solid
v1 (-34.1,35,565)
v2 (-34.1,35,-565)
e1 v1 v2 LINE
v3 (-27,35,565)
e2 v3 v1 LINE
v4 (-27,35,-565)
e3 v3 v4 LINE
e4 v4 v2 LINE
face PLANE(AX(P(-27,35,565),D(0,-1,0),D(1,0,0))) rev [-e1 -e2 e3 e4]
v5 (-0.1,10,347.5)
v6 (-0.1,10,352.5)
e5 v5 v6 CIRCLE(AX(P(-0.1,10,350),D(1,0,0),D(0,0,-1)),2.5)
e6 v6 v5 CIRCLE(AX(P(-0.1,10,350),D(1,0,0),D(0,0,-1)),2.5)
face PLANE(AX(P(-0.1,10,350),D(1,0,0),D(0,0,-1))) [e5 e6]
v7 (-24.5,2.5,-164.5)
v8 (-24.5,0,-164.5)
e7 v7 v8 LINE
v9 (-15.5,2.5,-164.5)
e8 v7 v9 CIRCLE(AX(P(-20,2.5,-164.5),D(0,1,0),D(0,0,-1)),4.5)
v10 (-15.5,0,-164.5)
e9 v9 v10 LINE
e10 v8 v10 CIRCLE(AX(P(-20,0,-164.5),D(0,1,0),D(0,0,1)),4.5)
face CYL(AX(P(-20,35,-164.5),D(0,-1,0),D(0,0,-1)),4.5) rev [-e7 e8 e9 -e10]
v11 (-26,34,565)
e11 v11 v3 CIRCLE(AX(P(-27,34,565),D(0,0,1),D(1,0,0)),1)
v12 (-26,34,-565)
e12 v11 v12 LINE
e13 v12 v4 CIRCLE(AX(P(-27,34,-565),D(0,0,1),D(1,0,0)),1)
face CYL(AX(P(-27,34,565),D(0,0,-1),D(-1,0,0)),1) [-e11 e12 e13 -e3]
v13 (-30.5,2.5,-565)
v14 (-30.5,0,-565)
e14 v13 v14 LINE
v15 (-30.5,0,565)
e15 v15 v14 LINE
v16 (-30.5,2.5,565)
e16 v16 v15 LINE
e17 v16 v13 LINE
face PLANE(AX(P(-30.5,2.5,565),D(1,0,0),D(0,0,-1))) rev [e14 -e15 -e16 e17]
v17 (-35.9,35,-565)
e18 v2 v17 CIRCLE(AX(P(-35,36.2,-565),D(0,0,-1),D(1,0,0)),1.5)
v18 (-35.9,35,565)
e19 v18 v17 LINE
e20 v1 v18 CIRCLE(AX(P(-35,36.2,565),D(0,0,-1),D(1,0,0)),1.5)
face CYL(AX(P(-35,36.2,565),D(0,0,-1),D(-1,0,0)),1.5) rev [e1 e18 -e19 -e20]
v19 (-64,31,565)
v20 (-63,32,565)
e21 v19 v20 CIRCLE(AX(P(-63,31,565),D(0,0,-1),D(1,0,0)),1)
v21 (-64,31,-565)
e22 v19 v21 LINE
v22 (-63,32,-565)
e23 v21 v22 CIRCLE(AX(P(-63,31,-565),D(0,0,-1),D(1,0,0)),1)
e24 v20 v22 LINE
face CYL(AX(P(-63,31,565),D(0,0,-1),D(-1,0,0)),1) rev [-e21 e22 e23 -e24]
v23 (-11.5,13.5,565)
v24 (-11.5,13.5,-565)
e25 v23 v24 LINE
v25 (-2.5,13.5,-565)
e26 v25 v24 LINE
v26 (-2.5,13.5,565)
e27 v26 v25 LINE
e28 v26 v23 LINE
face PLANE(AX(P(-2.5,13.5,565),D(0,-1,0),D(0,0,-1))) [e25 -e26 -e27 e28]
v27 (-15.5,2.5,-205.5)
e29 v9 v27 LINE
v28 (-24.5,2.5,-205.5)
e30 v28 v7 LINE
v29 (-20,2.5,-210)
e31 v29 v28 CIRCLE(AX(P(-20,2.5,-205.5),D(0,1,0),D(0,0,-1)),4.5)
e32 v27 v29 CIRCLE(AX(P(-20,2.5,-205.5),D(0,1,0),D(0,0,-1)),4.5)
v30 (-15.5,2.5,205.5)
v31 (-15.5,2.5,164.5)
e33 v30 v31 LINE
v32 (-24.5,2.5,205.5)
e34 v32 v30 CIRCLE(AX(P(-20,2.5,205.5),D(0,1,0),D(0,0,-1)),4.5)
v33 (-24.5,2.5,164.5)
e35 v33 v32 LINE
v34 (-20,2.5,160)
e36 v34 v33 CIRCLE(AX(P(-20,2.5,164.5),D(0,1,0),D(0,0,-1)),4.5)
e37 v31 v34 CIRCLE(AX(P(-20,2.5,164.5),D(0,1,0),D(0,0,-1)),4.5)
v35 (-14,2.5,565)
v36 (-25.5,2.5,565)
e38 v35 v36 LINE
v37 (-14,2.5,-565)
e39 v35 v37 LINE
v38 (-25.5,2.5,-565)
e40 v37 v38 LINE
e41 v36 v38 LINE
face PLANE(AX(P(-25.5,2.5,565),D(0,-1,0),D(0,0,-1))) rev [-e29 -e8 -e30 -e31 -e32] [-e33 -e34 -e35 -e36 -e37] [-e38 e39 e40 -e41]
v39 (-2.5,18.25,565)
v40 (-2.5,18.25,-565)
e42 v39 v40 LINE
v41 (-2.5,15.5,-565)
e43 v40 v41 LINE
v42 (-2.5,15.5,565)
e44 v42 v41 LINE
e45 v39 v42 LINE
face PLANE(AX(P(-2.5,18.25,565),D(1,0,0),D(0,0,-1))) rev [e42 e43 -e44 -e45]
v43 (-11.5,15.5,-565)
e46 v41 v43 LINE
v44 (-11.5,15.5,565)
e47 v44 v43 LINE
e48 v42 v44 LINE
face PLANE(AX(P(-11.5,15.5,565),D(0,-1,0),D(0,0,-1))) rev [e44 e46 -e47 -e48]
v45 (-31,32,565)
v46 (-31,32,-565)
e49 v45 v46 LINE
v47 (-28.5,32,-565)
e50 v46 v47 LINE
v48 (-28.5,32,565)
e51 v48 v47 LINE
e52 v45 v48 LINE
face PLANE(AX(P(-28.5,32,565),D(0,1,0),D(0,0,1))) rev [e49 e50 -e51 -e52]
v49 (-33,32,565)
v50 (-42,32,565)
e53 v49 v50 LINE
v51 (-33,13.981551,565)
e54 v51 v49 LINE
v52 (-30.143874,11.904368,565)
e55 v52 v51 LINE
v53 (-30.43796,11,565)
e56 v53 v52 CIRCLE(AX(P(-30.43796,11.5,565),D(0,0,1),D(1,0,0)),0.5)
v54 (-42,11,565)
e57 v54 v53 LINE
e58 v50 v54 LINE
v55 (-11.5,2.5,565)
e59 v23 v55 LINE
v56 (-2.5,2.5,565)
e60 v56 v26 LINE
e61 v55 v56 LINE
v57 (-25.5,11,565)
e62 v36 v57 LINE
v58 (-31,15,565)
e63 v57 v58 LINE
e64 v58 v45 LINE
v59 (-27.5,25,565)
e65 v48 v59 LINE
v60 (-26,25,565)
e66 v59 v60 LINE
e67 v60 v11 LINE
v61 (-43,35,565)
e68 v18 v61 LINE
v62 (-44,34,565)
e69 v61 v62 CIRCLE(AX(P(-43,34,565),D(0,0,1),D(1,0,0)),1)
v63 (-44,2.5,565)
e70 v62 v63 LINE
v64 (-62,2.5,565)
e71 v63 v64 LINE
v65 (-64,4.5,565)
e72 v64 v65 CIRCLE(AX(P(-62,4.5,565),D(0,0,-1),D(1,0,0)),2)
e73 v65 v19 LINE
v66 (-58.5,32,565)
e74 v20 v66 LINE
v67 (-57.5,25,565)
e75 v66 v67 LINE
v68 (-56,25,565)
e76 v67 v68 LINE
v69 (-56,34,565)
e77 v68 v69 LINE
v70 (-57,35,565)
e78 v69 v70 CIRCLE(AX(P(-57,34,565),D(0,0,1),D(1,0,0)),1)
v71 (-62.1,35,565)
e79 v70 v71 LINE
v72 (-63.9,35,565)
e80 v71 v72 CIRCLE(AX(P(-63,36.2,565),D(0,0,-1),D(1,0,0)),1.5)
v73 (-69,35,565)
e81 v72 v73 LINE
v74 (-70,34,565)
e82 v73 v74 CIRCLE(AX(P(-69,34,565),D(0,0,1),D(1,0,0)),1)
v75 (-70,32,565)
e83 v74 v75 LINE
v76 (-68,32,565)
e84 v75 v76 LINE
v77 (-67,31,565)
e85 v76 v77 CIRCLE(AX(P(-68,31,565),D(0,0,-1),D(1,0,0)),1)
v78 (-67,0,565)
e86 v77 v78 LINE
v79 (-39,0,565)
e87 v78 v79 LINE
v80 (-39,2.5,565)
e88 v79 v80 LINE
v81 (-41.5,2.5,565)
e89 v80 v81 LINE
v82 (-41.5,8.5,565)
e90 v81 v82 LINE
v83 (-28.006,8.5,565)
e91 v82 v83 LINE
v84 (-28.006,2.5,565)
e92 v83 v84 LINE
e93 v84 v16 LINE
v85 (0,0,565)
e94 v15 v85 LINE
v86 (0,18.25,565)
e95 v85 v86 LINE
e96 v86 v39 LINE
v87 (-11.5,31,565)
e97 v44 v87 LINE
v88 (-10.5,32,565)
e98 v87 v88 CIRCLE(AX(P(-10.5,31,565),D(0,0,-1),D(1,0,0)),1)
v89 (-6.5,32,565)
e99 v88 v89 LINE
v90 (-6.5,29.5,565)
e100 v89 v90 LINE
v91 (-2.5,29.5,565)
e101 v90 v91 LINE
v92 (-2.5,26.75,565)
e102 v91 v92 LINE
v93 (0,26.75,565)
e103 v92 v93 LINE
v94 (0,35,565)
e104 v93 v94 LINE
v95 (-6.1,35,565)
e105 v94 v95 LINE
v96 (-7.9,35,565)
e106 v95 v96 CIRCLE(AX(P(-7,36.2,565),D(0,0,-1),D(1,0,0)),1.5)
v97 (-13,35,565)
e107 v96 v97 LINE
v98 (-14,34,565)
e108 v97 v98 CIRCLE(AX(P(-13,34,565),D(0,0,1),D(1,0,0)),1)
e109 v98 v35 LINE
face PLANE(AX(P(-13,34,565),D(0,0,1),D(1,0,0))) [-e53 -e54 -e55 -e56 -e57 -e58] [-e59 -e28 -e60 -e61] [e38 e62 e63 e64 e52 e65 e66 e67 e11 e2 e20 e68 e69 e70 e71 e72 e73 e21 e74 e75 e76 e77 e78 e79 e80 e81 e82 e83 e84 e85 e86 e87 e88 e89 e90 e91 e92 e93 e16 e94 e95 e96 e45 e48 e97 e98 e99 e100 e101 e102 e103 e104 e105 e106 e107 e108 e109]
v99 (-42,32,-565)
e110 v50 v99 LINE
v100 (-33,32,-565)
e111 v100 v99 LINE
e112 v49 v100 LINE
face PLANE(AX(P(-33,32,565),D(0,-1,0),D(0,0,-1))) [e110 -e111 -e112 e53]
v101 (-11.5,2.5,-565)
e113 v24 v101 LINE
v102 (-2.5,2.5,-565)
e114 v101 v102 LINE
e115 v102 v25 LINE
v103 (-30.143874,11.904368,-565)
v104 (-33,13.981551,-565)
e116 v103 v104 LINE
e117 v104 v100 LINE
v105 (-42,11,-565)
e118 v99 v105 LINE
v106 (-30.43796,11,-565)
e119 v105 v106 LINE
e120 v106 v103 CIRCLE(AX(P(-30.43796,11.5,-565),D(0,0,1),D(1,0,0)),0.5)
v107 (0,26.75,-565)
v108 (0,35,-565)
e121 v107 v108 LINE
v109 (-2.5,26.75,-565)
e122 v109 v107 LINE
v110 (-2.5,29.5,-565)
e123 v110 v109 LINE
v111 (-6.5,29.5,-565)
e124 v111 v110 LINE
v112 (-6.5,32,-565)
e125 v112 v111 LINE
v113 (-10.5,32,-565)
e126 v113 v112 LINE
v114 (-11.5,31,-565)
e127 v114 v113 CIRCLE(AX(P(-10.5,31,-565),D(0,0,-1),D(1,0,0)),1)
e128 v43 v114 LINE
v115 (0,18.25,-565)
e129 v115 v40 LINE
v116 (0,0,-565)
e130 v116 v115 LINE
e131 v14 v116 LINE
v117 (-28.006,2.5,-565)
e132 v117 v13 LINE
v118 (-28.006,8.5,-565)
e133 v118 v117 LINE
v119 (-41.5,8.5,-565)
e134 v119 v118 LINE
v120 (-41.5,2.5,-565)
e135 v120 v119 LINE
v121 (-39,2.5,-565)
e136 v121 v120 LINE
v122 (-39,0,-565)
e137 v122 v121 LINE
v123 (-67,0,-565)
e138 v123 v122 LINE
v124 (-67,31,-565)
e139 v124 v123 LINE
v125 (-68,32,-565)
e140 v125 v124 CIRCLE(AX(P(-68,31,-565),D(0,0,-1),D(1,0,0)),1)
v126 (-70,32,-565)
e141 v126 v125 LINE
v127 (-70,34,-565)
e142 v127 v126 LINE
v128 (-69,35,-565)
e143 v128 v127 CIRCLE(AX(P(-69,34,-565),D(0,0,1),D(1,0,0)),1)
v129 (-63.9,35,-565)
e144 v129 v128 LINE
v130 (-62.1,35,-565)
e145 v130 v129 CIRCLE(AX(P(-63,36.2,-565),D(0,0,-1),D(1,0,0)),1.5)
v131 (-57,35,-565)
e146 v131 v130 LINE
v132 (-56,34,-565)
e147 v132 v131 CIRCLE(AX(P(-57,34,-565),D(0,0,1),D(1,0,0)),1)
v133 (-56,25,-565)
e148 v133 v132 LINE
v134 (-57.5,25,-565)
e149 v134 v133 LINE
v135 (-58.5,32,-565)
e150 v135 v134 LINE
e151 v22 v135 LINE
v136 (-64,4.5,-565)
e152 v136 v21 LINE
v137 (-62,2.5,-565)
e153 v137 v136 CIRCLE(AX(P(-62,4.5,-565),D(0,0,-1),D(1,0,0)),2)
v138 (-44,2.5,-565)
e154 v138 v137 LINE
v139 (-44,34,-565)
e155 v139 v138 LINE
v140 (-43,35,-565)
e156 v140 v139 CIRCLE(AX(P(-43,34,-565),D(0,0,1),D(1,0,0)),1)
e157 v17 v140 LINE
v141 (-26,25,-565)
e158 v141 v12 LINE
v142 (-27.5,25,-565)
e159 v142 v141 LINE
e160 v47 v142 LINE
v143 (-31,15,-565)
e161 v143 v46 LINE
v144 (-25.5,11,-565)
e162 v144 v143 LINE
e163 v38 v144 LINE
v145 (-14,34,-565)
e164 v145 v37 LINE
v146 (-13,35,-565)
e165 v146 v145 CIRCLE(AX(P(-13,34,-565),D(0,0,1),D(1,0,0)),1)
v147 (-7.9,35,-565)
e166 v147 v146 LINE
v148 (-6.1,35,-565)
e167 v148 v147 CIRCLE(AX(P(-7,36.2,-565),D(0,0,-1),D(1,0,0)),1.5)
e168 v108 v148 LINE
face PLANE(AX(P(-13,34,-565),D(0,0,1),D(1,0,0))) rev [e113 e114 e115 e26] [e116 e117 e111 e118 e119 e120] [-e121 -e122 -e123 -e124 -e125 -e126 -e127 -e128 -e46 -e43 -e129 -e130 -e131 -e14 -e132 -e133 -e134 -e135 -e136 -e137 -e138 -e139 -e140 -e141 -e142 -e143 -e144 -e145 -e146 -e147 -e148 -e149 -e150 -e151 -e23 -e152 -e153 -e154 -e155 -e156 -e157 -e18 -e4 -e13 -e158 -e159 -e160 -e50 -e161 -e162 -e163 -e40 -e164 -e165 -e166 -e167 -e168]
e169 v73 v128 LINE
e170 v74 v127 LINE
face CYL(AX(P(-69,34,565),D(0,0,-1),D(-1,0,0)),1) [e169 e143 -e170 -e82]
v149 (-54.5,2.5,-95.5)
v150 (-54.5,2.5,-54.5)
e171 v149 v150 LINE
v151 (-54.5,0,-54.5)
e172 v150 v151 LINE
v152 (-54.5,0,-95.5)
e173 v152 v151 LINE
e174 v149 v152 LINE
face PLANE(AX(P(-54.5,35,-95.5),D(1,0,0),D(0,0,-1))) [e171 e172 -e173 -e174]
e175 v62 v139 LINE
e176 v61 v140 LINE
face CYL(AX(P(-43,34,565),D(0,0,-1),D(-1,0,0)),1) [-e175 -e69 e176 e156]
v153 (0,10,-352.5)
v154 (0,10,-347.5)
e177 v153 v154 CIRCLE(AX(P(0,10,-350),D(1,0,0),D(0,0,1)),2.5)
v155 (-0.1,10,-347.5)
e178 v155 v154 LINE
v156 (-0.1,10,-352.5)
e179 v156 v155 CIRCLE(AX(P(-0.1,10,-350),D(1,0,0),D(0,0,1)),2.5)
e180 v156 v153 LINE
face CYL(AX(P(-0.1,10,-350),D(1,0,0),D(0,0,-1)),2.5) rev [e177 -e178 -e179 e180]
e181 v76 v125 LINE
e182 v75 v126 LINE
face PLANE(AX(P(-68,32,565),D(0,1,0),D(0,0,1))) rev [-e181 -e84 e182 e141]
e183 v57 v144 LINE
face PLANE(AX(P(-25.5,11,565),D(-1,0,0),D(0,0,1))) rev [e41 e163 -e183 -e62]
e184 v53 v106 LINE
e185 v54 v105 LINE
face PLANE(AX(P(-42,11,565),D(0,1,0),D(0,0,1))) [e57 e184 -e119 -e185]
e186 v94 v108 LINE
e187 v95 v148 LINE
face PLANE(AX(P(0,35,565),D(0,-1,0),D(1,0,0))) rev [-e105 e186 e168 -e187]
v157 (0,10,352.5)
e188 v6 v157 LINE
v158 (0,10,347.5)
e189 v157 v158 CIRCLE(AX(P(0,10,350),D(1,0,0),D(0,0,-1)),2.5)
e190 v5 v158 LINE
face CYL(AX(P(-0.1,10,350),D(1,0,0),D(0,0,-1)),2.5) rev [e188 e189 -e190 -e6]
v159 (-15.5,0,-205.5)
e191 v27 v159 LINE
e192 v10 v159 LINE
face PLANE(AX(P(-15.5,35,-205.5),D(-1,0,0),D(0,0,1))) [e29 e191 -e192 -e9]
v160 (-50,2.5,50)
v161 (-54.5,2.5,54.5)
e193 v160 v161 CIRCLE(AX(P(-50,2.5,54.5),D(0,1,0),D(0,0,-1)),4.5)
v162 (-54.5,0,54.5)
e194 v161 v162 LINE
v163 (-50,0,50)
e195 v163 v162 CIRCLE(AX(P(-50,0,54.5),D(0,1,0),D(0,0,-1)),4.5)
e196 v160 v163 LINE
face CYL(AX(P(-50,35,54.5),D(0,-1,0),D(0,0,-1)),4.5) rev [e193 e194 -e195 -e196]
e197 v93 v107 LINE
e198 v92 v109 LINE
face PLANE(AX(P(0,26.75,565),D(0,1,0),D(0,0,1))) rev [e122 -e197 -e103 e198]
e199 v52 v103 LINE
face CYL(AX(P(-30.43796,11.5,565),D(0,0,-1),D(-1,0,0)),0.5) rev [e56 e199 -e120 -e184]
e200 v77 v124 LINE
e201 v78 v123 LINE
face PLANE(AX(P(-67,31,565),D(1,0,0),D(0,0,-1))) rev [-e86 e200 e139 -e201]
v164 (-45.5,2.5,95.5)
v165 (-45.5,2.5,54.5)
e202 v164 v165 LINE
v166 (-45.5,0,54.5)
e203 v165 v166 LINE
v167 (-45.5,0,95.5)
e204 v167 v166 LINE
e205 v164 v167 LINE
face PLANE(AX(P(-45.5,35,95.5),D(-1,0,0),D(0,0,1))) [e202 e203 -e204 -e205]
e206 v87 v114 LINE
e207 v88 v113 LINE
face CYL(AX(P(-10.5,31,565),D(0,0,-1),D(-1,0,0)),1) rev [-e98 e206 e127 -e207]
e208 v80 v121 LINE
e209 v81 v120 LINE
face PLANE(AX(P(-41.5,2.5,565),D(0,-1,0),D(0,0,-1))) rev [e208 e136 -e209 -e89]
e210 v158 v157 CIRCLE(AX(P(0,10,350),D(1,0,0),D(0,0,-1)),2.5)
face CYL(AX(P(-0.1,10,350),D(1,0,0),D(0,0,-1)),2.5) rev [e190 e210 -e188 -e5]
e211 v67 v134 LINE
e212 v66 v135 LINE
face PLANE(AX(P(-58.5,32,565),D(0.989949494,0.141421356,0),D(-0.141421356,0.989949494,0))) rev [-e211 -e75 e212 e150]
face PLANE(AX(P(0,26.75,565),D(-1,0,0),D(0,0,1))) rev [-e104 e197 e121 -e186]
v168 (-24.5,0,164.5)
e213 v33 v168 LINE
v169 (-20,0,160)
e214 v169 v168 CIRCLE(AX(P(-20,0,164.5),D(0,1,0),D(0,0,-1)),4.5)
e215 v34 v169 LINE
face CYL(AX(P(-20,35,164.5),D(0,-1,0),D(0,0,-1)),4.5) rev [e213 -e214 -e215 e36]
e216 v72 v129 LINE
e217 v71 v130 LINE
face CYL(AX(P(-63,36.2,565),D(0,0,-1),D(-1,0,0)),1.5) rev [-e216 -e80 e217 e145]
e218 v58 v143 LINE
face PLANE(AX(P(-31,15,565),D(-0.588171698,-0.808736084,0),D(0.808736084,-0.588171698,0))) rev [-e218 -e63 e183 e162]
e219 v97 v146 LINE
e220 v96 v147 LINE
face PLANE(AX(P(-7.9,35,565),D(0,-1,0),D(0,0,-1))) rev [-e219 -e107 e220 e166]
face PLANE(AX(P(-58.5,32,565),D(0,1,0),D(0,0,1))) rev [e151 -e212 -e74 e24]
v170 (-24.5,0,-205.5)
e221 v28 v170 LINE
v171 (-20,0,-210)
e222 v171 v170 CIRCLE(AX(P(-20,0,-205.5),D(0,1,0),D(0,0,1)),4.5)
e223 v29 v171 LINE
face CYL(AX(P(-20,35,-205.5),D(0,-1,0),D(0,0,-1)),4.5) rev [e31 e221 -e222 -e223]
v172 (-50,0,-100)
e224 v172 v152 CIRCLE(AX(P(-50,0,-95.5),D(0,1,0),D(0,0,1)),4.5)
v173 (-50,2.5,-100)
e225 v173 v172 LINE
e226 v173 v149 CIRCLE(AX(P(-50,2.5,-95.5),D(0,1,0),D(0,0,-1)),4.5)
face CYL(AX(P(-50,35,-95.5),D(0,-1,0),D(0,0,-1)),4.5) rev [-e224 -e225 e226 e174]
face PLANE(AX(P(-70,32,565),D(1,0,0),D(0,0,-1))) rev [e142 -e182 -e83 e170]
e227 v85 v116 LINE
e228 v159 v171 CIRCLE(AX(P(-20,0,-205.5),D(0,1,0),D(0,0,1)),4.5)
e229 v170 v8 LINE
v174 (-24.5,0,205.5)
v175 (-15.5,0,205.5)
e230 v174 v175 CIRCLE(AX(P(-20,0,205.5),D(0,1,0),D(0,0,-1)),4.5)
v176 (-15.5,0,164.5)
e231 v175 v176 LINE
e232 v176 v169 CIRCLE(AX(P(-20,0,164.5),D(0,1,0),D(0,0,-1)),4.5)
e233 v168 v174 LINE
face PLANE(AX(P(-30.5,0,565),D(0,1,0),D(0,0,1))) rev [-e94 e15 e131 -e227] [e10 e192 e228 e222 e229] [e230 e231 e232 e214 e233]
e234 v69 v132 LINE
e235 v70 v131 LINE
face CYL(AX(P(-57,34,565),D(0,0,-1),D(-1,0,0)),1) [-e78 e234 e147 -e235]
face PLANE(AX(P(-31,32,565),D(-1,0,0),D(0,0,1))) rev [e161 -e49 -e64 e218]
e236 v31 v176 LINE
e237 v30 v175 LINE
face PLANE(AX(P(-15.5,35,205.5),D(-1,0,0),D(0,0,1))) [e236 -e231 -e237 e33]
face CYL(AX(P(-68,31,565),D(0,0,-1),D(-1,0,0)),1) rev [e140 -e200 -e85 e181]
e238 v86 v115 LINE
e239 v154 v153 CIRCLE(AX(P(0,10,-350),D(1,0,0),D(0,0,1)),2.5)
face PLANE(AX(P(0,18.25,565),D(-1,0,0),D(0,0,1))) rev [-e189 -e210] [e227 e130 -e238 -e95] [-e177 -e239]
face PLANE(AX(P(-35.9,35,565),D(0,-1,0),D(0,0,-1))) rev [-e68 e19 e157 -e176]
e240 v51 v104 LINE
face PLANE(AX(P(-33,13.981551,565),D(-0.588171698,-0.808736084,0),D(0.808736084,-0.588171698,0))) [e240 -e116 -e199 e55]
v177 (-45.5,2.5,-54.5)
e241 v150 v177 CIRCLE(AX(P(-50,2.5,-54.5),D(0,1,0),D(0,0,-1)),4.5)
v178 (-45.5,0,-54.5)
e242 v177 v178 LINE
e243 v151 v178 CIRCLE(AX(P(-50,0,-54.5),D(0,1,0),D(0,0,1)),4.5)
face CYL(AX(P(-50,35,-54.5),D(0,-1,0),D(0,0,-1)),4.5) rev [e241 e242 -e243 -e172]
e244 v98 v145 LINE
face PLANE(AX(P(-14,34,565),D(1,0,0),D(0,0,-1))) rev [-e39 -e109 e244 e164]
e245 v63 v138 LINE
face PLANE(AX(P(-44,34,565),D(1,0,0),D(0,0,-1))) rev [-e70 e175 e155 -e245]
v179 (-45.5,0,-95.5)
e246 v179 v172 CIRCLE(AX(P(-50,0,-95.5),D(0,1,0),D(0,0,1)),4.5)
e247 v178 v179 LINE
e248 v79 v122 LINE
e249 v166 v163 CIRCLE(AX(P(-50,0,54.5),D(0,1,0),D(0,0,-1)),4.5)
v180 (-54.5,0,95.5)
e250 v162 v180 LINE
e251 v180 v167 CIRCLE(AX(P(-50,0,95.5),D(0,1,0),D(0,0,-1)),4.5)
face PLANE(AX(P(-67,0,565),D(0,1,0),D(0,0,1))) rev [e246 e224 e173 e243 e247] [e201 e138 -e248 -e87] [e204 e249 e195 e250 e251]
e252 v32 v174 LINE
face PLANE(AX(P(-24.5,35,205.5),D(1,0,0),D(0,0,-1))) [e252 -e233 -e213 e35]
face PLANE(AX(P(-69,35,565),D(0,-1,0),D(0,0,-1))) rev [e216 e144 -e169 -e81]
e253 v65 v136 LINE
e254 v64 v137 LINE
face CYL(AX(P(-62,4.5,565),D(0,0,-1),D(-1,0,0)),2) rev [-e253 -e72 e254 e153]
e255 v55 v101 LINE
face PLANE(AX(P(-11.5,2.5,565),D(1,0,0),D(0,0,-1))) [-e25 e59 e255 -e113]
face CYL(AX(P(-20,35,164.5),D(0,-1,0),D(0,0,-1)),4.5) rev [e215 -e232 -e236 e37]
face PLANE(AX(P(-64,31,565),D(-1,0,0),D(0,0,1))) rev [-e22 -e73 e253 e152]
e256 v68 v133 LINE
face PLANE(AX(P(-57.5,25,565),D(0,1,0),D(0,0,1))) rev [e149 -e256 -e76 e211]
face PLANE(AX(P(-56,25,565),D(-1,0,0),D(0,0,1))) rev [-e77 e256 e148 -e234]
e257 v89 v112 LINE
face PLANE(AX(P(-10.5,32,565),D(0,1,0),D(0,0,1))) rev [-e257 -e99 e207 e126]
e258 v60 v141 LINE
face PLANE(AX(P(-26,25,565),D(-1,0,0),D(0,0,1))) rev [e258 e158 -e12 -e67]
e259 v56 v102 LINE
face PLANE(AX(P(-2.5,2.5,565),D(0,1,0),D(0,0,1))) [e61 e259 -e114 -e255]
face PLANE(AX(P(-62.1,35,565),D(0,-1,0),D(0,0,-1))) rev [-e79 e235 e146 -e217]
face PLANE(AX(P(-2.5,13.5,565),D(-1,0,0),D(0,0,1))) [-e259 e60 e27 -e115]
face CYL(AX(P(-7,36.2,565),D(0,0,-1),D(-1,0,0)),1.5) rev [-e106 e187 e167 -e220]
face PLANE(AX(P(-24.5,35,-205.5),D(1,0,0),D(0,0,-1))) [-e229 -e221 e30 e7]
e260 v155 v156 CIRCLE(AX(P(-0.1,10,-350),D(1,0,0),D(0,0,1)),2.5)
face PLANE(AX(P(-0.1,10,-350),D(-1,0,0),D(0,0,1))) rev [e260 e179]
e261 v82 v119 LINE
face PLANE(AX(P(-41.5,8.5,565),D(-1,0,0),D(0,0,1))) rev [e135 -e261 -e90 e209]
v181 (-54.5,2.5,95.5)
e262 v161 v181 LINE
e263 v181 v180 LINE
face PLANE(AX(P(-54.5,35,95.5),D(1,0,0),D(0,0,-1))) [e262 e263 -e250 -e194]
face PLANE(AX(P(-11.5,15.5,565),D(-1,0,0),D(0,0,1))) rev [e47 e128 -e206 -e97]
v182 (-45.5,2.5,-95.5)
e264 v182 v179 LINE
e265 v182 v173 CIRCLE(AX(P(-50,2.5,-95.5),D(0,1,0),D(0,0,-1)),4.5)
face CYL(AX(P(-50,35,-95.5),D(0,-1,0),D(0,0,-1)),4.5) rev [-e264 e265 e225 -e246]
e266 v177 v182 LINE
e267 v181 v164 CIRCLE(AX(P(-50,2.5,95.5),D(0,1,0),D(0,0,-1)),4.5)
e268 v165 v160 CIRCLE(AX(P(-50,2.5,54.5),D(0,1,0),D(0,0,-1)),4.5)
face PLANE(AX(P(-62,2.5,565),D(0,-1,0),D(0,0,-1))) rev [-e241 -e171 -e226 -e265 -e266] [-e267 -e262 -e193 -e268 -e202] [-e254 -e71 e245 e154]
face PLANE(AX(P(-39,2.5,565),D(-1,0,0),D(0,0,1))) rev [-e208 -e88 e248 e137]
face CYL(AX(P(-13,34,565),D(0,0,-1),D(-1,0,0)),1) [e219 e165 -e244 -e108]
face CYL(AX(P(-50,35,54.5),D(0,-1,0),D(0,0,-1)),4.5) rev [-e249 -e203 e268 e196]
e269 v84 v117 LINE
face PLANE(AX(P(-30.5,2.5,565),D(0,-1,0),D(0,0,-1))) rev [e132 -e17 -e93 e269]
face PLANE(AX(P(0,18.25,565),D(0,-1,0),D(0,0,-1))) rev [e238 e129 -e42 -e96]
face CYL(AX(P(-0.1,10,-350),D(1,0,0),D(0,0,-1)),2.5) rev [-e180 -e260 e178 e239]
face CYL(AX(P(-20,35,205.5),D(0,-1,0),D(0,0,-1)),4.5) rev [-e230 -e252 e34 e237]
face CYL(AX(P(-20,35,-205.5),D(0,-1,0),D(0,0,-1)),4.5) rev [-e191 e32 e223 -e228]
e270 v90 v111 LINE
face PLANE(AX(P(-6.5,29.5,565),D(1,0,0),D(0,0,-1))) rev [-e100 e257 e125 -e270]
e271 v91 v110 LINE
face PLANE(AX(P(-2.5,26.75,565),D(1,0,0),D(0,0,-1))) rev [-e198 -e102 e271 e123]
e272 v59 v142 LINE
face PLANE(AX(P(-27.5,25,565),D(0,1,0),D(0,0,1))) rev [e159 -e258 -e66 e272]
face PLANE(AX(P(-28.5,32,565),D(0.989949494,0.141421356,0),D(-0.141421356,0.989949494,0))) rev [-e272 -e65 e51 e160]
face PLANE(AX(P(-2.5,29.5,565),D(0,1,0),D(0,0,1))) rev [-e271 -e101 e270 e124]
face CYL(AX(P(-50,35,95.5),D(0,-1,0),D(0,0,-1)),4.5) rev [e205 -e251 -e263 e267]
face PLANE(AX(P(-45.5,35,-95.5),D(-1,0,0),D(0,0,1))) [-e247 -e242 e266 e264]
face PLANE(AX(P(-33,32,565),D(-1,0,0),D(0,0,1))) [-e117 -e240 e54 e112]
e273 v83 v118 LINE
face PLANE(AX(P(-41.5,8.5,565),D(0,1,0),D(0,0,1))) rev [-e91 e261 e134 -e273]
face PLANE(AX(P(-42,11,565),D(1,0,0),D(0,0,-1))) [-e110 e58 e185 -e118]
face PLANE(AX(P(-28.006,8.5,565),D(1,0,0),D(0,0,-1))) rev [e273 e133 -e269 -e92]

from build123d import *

# Parameters (mm, degrees)
SKETCH_1_W               = 9
SKETCH_1_H               = 11
EXTRUDE_1_DEPTH          = 565
CUT_EXTRUDE_1_DEPTH      = 571.246657158
CUT_EXTRUDE_1_DEPTH_BACK = 571.246657158
SKETCH_3_R               = 2.5
CUT_EXTRUDE_2_DEPTH      = 0.1


with BuildPart() as part:
    # 草图1 → 凸台-拉伸1 (new, symmetric)
    with BuildSketch(Plane.XY):
        with BuildLine():
            Line((-28.5, 32), (-27.5, 25))
            Line((-27.5, 25), (-26, 25))
            Line((-26, 25), (-26, 34))
            ThreePointArc((-26, 34), (-26.292893219, 34.707106781), (-27, 35))
            Line((-27, 35), (-34.1, 35))
            ThreePointArc((-34.1, 35), (-35, 34.7), (-35.9, 35))
            Line((-35.9, 35), (-43, 35))
            ThreePointArc((-43, 35), (-43.707106781, 34.707106781), (-44, 34))
            Line((-44, 34), (-44, 2.5))
            Line((-44, 2.5), (-62, 2.5))
            ThreePointArc((-62, 2.5), (-63.414213562, 3.085786438), (-64, 4.5))
            Line((-64, 4.5), (-64, 31))
            ThreePointArc((-64, 31), (-63.707106781, 31.707106781), (-63, 32))
            Line((-63, 32), (-58.5, 32))
            Line((-58.5, 32), (-57.5, 25))
            Line((-57.5, 25), (-56, 25))
            Line((-56, 25), (-56, 34))
            ThreePointArc((-56, 34), (-56.292893219, 34.707106781), (-57, 35))
            Line((-57, 35), (-62.1, 35))
            ThreePointArc((-62.1, 35), (-63, 34.7), (-63.9, 35))
            Line((-63.9, 35), (-69, 35))
            ThreePointArc((-69, 35), (-69.707106781, 34.707106781), (-70, 34))
            Line((-70, 34), (-70, 32))
            Line((-70, 32), (-68, 32))
            ThreePointArc((-68, 32), (-67.292893219, 31.707106781), (-67, 31))
            Line((-67, 31), (-67, 0))
            Line((-67, 0), (-39, 0))
            Line((-39, 0), (-39, 2.5))
            Line((-39, 2.5), (-41.5, 2.5))
            Line((-41.5, 2.5), (-41.5, 8.5))
            Line((-41.5, 8.5), (-28.006, 8.5))
            Line((-28.006, 8.5), (-28.006, 2.5))
            Line((-28.006, 2.5), (-30.5, 2.5))
            Line((-30.5, 2.5), (-30.5, 0))
            Line((-30.5, 0), (0, 0))
            Line((0, 0), (0, 18.25))
            Line((0, 18.25), (-2.5, 18.25))
            Line((-2.5, 18.25), (-2.5, 15.5))
            Line((-2.5, 15.5), (-11.5, 15.5))
            Line((-11.5, 15.5), (-11.5, 31))
            ThreePointArc((-11.5, 31), (-11.207106781, 31.707106781), (-10.5, 32))
            Line((-10.5, 32), (-6.5, 32))
            Line((-6.5, 32), (-6.5, 29.5))
            Line((-6.5, 29.5), (-2.5, 29.5))
            Line((-2.5, 29.5), (-2.5, 26.75))
            Line((-2.5, 26.75), (0, 26.75))
            Line((0, 26.75), (0, 35))
            Line((0, 35), (-6.1, 35))
            ThreePointArc((-6.1, 35), (-7, 34.7), (-7.9, 35))
            Line((-7.9, 35), (-13, 35))
            ThreePointArc((-13, 35), (-13.707106781, 34.707106781), (-14, 34))
            Line((-14, 34), (-14, 2.5))
            Line((-14, 2.5), (-25.5, 2.5))
            Line((-25.5, 2.5), (-25.5, 11))
            Line((-25.5, 11), (-31, 15))
            Line((-31, 15), (-31, 32))
            Line((-31, 32), (-28.5, 32))
        make_face()
        with Locations((-7, 8)):
            Rectangle(SKETCH_1_W, SKETCH_1_H, mode=Mode.SUBTRACT)
        with BuildLine():
            Line((-42, 11), (-42, 32))
            Line((-42, 32), (-33, 32))
            Line((-33, 32), (-33, 13.981550817))
            Line((-33, 13.981550817), (-30.143873685, 11.904368042))
            ThreePointArc((-30.143873685, 11.904368042), (-29.962468198, 11.345377914), (-30.437959534, 11))
            Line((-30.437959534, 11), (-42, 11))
        make_face(mode=Mode.SUBTRACT)
    extrude(amount=EXTRUDE_1_DEPTH, both=True)

    # 草图2 → 切除-拉伸1 (cut, two sides: drawn at the far end of the back side and taken through both)
    with BuildSketch(Plane(origin=(0, 2.5, 0), x_dir=(1, 0, 0), z_dir=(0, 1, 0)).offset(-CUT_EXTRUDE_1_DEPTH_BACK)):
        with BuildLine():
            Line((-15.5, -205.5), (-15.5, -164.5))
            ThreePointArc((-15.5, -164.5), (-20, -160), (-24.5, -164.5))
            Line((-24.5, -164.5), (-24.5, -205.5))
            ThreePointArc((-24.5, -205.5), (-20, -210), (-15.5, -205.5))
        make_face()
        with BuildLine():
            Line((-45.5, 95.5), (-45.5, 54.5))
            ThreePointArc((-45.5, 54.5), (-50, 50), (-54.5, 54.5))
            Line((-54.5, 54.5), (-54.5, 95.5))
            ThreePointArc((-54.5, 95.5), (-50, 100), (-45.5, 95.5))
        make_face()
        with BuildLine():
            Line((-45.5, -95.5), (-45.5, -54.5))
            ThreePointArc((-45.5, -54.5), (-50, -50), (-54.5, -54.5))
            Line((-54.5, -54.5), (-54.5, -95.5))
            ThreePointArc((-54.5, -95.5), (-50, -100), (-45.5, -95.5))
        make_face()
        with BuildLine():
            Line((-15.5, 205.5), (-15.5, 164.5))
            ThreePointArc((-15.5, 164.5), (-20, 160), (-24.5, 164.5))
            Line((-24.5, 164.5), (-24.5, 205.5))
            ThreePointArc((-24.5, 205.5), (-20, 210), (-15.5, 205.5))
        make_face()
    extrude(amount=CUT_EXTRUDE_1_DEPTH + CUT_EXTRUDE_1_DEPTH_BACK, mode=Mode.SUBTRACT)

    # 草图3 → 切除-拉伸2 (cut)
    with BuildSketch(Plane(origin=(0, 0, 0), x_dir=(0, 0, -1), z_dir=(1, 0, 0))):
        with Locations((-350, 10)):
            Circle(SKETCH_3_R)
        with Locations(Location((350, 10, 0), (0, 0, 180))):
            Circle(SKETCH_3_R)
    extrude(amount=-CUT_EXTRUDE_2_DEPTH, mode=Mode.SUBTRACT)


solid = part.part
